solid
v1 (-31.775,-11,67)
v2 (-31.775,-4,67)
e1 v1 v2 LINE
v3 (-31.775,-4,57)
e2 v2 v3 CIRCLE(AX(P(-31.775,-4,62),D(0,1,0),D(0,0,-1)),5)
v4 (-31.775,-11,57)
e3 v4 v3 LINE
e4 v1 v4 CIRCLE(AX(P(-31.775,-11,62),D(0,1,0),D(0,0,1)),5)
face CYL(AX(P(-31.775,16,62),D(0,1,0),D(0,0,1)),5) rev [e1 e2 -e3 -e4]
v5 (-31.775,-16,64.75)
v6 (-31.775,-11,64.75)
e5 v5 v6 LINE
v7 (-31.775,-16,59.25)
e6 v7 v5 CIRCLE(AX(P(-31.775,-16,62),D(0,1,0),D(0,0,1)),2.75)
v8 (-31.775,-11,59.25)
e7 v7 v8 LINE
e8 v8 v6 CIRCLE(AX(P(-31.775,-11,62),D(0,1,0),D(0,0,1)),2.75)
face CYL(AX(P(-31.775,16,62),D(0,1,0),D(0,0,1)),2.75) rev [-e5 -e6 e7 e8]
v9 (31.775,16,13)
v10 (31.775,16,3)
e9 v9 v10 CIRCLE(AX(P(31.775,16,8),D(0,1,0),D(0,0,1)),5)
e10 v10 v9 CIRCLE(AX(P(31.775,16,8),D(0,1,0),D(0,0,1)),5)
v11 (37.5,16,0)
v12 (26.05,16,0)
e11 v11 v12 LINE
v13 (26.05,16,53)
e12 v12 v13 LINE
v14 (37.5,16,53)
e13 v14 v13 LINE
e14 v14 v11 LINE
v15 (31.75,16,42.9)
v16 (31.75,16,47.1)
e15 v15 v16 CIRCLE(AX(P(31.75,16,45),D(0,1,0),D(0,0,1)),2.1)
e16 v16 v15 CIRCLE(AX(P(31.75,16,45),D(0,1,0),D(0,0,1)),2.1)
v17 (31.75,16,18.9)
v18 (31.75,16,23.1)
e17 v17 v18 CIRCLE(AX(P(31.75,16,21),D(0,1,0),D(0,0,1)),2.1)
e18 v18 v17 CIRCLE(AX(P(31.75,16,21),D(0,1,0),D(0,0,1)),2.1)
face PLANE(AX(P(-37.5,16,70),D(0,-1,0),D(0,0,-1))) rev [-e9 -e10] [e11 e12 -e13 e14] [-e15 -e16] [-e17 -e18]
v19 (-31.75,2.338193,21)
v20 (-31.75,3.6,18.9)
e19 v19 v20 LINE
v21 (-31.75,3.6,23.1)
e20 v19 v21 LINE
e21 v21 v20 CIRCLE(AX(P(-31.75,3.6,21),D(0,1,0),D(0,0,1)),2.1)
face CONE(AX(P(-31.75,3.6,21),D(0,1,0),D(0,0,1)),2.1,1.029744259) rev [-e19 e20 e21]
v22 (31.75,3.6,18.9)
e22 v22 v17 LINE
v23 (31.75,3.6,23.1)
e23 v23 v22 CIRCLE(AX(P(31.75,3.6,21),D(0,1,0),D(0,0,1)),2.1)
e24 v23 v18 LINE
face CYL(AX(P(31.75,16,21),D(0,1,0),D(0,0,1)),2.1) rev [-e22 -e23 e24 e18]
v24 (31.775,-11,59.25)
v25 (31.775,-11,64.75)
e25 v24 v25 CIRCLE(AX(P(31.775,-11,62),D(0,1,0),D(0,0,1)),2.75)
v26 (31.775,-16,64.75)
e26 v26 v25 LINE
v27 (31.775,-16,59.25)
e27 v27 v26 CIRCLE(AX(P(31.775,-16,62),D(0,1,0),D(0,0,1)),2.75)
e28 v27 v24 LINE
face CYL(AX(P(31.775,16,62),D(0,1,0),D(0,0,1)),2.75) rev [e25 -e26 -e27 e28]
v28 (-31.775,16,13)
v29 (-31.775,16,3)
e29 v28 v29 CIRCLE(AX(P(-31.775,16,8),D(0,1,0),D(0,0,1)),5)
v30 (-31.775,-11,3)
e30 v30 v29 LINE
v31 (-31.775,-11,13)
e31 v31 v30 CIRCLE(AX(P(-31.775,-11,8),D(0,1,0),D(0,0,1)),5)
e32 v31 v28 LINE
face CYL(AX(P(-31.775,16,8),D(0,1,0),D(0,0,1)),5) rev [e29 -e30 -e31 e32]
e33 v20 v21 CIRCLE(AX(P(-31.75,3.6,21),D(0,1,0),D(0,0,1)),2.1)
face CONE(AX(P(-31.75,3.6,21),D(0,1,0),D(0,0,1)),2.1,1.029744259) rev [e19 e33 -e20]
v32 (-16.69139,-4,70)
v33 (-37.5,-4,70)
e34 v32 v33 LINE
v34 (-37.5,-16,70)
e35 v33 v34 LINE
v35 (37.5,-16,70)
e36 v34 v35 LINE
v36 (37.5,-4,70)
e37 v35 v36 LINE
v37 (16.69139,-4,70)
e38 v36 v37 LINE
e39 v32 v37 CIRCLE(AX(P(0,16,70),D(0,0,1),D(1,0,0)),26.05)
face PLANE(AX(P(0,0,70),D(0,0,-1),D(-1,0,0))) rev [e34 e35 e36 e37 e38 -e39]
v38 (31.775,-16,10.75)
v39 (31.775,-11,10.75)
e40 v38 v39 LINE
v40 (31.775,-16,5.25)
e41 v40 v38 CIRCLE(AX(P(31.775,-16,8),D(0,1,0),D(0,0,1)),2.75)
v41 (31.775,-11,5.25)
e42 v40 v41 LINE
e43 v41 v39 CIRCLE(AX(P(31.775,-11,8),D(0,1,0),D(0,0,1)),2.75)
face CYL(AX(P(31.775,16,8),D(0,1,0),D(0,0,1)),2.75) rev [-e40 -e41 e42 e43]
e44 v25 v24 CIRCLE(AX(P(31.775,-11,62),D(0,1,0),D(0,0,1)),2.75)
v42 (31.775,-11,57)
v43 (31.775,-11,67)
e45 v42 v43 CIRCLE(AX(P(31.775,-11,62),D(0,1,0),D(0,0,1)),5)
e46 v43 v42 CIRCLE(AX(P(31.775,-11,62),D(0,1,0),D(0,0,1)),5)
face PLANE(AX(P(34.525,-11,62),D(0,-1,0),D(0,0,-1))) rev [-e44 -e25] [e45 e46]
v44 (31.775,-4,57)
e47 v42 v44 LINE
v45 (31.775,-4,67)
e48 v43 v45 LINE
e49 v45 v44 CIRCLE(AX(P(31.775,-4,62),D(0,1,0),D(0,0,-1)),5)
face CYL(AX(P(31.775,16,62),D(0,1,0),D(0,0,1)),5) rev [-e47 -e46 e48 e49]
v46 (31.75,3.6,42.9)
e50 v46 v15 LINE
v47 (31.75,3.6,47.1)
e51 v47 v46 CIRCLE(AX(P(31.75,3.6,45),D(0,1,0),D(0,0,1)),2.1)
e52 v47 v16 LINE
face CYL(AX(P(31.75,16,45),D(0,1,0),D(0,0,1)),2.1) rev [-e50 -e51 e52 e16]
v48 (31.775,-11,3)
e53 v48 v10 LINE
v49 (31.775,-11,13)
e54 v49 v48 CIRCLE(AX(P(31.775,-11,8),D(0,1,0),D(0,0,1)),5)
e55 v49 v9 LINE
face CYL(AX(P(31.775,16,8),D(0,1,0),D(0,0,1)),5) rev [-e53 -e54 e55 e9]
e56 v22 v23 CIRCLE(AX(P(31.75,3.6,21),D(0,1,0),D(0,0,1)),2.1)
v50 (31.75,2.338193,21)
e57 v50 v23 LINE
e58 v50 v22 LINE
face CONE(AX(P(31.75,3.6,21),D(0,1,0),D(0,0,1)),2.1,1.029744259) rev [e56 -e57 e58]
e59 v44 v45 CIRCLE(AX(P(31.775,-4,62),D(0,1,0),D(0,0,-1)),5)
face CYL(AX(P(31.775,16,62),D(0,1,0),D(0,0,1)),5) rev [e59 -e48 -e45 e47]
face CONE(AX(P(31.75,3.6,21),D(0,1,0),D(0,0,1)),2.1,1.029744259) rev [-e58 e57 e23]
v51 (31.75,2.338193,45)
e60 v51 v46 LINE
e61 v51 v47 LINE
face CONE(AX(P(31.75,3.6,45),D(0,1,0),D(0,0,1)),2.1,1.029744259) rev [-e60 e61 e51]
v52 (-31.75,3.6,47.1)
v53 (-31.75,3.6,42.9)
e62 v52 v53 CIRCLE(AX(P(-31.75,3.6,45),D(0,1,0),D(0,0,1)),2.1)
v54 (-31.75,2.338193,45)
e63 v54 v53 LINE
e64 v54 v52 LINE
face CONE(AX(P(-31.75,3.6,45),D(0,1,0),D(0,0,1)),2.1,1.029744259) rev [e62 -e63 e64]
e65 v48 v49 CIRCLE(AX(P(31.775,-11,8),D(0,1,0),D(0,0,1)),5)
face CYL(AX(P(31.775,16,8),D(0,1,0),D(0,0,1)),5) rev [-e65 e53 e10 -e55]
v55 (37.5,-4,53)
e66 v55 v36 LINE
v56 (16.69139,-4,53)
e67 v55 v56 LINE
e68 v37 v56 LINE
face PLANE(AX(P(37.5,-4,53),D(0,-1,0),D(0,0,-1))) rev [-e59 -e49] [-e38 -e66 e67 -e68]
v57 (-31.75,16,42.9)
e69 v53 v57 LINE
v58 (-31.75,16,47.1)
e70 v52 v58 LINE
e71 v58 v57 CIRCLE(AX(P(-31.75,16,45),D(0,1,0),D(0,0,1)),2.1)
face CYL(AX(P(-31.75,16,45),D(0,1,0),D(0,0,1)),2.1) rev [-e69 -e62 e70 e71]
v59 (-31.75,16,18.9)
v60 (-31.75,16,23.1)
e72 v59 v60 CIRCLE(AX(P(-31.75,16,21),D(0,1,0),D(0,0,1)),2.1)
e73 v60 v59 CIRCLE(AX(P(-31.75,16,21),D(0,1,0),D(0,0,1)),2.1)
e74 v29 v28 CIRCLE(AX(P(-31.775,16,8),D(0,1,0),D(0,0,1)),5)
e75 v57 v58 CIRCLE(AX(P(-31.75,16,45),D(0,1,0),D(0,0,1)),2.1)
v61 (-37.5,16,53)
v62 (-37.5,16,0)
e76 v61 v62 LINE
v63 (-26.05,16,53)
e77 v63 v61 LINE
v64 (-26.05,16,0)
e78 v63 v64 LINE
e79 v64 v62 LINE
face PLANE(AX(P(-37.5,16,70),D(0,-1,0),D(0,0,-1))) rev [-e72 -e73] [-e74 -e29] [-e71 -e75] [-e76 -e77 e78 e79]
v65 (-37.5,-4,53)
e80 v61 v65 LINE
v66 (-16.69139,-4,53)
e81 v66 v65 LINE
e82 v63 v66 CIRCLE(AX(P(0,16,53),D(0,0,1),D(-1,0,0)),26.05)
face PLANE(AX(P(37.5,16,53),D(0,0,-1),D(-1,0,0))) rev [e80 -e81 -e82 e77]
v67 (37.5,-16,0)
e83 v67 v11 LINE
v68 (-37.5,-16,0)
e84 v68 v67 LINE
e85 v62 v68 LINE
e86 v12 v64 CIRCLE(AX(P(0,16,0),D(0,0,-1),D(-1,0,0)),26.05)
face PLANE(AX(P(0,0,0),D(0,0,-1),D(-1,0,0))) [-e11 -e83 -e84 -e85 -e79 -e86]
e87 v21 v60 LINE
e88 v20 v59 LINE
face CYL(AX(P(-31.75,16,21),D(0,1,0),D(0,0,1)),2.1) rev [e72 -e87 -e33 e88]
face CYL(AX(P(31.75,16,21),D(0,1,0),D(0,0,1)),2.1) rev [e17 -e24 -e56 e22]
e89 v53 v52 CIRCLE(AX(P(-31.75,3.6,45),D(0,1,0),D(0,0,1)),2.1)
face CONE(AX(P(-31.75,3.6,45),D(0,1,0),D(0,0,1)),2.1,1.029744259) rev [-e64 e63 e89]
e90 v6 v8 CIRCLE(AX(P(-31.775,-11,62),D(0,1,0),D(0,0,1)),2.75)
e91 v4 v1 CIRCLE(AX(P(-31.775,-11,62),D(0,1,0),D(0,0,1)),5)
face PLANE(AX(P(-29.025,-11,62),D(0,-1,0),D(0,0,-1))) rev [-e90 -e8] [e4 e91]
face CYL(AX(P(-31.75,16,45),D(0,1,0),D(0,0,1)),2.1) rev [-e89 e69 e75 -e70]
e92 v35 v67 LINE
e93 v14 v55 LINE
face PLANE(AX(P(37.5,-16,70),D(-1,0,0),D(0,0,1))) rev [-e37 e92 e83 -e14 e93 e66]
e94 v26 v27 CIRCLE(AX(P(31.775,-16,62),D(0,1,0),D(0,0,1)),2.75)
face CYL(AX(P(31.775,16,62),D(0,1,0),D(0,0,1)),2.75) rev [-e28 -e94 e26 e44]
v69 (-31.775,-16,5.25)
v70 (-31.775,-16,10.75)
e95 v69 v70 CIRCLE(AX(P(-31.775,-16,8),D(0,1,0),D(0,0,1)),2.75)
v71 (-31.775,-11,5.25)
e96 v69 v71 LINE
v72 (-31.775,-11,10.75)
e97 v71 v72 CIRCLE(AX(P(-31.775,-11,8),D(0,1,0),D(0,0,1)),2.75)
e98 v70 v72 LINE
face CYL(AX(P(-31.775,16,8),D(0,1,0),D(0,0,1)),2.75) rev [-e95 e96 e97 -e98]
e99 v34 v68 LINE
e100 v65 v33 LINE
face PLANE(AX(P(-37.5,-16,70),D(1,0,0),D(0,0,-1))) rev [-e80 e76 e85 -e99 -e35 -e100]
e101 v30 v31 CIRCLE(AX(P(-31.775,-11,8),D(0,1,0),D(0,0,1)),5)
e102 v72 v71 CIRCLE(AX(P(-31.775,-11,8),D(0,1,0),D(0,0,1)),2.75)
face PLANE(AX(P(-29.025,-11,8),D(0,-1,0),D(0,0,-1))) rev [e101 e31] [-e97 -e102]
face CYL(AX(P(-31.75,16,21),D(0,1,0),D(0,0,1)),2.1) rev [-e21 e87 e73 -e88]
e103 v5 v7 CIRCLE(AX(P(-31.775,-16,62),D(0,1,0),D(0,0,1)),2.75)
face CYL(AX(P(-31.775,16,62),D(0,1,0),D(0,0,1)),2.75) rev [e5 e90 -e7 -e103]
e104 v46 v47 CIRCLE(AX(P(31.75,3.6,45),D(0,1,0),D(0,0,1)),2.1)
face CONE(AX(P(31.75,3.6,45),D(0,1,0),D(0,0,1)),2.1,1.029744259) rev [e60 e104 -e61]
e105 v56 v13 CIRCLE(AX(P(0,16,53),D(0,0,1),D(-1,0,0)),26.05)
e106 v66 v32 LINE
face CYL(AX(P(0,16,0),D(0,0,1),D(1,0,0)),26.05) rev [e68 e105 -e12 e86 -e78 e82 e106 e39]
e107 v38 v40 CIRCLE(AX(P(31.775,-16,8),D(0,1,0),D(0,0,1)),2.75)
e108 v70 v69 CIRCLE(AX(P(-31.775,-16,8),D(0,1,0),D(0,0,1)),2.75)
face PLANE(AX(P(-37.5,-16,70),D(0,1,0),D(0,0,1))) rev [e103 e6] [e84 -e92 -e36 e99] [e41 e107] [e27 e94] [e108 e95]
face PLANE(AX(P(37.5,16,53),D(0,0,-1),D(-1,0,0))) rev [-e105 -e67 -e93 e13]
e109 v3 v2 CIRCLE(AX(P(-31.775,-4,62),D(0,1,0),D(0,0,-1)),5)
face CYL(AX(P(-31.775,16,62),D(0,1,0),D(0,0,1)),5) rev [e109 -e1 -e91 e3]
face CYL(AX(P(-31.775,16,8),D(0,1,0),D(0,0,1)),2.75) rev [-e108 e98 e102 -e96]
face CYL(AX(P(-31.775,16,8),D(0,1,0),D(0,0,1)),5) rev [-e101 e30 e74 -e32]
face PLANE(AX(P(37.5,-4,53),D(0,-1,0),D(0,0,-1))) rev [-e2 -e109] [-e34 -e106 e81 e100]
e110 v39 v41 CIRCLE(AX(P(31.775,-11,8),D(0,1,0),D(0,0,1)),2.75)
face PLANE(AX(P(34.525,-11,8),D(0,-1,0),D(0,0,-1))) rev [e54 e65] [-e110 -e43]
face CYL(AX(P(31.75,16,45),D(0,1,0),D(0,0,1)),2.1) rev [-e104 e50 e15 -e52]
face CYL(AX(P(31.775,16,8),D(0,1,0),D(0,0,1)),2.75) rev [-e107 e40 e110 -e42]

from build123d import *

# Parameters (mm, degrees)
SKETCH_2_W                   = 75
SKETCH_2_H                   = 32
EXTRUDE_1_DEPTH              = 70
SKETCH_4_R                   = 26.05
CUT_EXTRUDE_1_DEPTH          = 82.007715682
HOLE_WIZARD_M5_1_D           = 5.5
HOLE_WIZARD_M5_1_CBORE_D     = 10
HOLE_WIZARD_M5_1_CBORE_DEPTH = 27
SKETCH_7_W                   = 17
SKETCH_7_H                   = 20
CUT_EXTRUDE_2_DEPTH          = 104.831594421
HOLE_WIZARD_M5_1_2_D         = 4.2
HOLE_WIZARD_M5_1_2_DEPTH     = 12.4
HOLE_WIZARD_M5_1_2_TIP       = 1.2618073


with BuildPart() as part:
    # 草图2 → 凸台-拉伸1 (new body)
    with BuildSketch(Plane.XY):
        Rectangle(SKETCH_2_W, SKETCH_2_H)
    extrude(amount=EXTRUDE_1_DEPTH)

    # 草图4 → 切除-拉伸1 (cut, through all)
    with BuildSketch(Plane.XY.offset(70)):
        with Locations((0, 16)):
            Circle(SKETCH_4_R)
    extrude(amount=-CUT_EXTRUDE_1_DEPTH, mode=Mode.SUBTRACT)

    # Hole Wizard M5 _1 (through all)
    with Locations(Plane(origin=(0, 16, 0), x_dir=(1, 0, 0), z_dir=(0, 1, 0))):
        with Locations((-31.775, -8), (-31.775, -62), (31.775, -62), (31.775, -8)):
            CounterBoreHole(HOLE_WIZARD_M5_1_D / 2, HOLE_WIZARD_M5_1_CBORE_D / 2, HOLE_WIZARD_M5_1_CBORE_DEPTH)

    # 草图7 → 切除-拉伸2 (cut, through all)
    with BuildSketch(Plane.ZY.offset(37.5)):
        with Locations((61.5, 6)):
            Rectangle(SKETCH_7_W, SKETCH_7_H)
    extrude(amount=-CUT_EXTRUDE_2_DEPTH, mode=Mode.SUBTRACT)

    # Hole Wizard M5 _1 2
    with Locations(Plane(origin=(0, 16, 0), x_dir=(1, 0, 0), z_dir=(0, 1, 0))):
        with Locations((-31.75, -21), (-31.75, -45), (31.75, -21), (31.75, -45)):
            Hole(HOLE_WIZARD_M5_1_2_D / 2, depth=HOLE_WIZARD_M5_1_2_DEPTH)
            with Locations((0, 0, -(HOLE_WIZARD_M5_1_2_DEPTH + HOLE_WIZARD_M5_1_2_TIP / 2))):  # 118° drill point
                Cone(0, HOLE_WIZARD_M5_1_2_D / 2, HOLE_WIZARD_M5_1_2_TIP, mode=Mode.SUBTRACT)


solid = part.part
